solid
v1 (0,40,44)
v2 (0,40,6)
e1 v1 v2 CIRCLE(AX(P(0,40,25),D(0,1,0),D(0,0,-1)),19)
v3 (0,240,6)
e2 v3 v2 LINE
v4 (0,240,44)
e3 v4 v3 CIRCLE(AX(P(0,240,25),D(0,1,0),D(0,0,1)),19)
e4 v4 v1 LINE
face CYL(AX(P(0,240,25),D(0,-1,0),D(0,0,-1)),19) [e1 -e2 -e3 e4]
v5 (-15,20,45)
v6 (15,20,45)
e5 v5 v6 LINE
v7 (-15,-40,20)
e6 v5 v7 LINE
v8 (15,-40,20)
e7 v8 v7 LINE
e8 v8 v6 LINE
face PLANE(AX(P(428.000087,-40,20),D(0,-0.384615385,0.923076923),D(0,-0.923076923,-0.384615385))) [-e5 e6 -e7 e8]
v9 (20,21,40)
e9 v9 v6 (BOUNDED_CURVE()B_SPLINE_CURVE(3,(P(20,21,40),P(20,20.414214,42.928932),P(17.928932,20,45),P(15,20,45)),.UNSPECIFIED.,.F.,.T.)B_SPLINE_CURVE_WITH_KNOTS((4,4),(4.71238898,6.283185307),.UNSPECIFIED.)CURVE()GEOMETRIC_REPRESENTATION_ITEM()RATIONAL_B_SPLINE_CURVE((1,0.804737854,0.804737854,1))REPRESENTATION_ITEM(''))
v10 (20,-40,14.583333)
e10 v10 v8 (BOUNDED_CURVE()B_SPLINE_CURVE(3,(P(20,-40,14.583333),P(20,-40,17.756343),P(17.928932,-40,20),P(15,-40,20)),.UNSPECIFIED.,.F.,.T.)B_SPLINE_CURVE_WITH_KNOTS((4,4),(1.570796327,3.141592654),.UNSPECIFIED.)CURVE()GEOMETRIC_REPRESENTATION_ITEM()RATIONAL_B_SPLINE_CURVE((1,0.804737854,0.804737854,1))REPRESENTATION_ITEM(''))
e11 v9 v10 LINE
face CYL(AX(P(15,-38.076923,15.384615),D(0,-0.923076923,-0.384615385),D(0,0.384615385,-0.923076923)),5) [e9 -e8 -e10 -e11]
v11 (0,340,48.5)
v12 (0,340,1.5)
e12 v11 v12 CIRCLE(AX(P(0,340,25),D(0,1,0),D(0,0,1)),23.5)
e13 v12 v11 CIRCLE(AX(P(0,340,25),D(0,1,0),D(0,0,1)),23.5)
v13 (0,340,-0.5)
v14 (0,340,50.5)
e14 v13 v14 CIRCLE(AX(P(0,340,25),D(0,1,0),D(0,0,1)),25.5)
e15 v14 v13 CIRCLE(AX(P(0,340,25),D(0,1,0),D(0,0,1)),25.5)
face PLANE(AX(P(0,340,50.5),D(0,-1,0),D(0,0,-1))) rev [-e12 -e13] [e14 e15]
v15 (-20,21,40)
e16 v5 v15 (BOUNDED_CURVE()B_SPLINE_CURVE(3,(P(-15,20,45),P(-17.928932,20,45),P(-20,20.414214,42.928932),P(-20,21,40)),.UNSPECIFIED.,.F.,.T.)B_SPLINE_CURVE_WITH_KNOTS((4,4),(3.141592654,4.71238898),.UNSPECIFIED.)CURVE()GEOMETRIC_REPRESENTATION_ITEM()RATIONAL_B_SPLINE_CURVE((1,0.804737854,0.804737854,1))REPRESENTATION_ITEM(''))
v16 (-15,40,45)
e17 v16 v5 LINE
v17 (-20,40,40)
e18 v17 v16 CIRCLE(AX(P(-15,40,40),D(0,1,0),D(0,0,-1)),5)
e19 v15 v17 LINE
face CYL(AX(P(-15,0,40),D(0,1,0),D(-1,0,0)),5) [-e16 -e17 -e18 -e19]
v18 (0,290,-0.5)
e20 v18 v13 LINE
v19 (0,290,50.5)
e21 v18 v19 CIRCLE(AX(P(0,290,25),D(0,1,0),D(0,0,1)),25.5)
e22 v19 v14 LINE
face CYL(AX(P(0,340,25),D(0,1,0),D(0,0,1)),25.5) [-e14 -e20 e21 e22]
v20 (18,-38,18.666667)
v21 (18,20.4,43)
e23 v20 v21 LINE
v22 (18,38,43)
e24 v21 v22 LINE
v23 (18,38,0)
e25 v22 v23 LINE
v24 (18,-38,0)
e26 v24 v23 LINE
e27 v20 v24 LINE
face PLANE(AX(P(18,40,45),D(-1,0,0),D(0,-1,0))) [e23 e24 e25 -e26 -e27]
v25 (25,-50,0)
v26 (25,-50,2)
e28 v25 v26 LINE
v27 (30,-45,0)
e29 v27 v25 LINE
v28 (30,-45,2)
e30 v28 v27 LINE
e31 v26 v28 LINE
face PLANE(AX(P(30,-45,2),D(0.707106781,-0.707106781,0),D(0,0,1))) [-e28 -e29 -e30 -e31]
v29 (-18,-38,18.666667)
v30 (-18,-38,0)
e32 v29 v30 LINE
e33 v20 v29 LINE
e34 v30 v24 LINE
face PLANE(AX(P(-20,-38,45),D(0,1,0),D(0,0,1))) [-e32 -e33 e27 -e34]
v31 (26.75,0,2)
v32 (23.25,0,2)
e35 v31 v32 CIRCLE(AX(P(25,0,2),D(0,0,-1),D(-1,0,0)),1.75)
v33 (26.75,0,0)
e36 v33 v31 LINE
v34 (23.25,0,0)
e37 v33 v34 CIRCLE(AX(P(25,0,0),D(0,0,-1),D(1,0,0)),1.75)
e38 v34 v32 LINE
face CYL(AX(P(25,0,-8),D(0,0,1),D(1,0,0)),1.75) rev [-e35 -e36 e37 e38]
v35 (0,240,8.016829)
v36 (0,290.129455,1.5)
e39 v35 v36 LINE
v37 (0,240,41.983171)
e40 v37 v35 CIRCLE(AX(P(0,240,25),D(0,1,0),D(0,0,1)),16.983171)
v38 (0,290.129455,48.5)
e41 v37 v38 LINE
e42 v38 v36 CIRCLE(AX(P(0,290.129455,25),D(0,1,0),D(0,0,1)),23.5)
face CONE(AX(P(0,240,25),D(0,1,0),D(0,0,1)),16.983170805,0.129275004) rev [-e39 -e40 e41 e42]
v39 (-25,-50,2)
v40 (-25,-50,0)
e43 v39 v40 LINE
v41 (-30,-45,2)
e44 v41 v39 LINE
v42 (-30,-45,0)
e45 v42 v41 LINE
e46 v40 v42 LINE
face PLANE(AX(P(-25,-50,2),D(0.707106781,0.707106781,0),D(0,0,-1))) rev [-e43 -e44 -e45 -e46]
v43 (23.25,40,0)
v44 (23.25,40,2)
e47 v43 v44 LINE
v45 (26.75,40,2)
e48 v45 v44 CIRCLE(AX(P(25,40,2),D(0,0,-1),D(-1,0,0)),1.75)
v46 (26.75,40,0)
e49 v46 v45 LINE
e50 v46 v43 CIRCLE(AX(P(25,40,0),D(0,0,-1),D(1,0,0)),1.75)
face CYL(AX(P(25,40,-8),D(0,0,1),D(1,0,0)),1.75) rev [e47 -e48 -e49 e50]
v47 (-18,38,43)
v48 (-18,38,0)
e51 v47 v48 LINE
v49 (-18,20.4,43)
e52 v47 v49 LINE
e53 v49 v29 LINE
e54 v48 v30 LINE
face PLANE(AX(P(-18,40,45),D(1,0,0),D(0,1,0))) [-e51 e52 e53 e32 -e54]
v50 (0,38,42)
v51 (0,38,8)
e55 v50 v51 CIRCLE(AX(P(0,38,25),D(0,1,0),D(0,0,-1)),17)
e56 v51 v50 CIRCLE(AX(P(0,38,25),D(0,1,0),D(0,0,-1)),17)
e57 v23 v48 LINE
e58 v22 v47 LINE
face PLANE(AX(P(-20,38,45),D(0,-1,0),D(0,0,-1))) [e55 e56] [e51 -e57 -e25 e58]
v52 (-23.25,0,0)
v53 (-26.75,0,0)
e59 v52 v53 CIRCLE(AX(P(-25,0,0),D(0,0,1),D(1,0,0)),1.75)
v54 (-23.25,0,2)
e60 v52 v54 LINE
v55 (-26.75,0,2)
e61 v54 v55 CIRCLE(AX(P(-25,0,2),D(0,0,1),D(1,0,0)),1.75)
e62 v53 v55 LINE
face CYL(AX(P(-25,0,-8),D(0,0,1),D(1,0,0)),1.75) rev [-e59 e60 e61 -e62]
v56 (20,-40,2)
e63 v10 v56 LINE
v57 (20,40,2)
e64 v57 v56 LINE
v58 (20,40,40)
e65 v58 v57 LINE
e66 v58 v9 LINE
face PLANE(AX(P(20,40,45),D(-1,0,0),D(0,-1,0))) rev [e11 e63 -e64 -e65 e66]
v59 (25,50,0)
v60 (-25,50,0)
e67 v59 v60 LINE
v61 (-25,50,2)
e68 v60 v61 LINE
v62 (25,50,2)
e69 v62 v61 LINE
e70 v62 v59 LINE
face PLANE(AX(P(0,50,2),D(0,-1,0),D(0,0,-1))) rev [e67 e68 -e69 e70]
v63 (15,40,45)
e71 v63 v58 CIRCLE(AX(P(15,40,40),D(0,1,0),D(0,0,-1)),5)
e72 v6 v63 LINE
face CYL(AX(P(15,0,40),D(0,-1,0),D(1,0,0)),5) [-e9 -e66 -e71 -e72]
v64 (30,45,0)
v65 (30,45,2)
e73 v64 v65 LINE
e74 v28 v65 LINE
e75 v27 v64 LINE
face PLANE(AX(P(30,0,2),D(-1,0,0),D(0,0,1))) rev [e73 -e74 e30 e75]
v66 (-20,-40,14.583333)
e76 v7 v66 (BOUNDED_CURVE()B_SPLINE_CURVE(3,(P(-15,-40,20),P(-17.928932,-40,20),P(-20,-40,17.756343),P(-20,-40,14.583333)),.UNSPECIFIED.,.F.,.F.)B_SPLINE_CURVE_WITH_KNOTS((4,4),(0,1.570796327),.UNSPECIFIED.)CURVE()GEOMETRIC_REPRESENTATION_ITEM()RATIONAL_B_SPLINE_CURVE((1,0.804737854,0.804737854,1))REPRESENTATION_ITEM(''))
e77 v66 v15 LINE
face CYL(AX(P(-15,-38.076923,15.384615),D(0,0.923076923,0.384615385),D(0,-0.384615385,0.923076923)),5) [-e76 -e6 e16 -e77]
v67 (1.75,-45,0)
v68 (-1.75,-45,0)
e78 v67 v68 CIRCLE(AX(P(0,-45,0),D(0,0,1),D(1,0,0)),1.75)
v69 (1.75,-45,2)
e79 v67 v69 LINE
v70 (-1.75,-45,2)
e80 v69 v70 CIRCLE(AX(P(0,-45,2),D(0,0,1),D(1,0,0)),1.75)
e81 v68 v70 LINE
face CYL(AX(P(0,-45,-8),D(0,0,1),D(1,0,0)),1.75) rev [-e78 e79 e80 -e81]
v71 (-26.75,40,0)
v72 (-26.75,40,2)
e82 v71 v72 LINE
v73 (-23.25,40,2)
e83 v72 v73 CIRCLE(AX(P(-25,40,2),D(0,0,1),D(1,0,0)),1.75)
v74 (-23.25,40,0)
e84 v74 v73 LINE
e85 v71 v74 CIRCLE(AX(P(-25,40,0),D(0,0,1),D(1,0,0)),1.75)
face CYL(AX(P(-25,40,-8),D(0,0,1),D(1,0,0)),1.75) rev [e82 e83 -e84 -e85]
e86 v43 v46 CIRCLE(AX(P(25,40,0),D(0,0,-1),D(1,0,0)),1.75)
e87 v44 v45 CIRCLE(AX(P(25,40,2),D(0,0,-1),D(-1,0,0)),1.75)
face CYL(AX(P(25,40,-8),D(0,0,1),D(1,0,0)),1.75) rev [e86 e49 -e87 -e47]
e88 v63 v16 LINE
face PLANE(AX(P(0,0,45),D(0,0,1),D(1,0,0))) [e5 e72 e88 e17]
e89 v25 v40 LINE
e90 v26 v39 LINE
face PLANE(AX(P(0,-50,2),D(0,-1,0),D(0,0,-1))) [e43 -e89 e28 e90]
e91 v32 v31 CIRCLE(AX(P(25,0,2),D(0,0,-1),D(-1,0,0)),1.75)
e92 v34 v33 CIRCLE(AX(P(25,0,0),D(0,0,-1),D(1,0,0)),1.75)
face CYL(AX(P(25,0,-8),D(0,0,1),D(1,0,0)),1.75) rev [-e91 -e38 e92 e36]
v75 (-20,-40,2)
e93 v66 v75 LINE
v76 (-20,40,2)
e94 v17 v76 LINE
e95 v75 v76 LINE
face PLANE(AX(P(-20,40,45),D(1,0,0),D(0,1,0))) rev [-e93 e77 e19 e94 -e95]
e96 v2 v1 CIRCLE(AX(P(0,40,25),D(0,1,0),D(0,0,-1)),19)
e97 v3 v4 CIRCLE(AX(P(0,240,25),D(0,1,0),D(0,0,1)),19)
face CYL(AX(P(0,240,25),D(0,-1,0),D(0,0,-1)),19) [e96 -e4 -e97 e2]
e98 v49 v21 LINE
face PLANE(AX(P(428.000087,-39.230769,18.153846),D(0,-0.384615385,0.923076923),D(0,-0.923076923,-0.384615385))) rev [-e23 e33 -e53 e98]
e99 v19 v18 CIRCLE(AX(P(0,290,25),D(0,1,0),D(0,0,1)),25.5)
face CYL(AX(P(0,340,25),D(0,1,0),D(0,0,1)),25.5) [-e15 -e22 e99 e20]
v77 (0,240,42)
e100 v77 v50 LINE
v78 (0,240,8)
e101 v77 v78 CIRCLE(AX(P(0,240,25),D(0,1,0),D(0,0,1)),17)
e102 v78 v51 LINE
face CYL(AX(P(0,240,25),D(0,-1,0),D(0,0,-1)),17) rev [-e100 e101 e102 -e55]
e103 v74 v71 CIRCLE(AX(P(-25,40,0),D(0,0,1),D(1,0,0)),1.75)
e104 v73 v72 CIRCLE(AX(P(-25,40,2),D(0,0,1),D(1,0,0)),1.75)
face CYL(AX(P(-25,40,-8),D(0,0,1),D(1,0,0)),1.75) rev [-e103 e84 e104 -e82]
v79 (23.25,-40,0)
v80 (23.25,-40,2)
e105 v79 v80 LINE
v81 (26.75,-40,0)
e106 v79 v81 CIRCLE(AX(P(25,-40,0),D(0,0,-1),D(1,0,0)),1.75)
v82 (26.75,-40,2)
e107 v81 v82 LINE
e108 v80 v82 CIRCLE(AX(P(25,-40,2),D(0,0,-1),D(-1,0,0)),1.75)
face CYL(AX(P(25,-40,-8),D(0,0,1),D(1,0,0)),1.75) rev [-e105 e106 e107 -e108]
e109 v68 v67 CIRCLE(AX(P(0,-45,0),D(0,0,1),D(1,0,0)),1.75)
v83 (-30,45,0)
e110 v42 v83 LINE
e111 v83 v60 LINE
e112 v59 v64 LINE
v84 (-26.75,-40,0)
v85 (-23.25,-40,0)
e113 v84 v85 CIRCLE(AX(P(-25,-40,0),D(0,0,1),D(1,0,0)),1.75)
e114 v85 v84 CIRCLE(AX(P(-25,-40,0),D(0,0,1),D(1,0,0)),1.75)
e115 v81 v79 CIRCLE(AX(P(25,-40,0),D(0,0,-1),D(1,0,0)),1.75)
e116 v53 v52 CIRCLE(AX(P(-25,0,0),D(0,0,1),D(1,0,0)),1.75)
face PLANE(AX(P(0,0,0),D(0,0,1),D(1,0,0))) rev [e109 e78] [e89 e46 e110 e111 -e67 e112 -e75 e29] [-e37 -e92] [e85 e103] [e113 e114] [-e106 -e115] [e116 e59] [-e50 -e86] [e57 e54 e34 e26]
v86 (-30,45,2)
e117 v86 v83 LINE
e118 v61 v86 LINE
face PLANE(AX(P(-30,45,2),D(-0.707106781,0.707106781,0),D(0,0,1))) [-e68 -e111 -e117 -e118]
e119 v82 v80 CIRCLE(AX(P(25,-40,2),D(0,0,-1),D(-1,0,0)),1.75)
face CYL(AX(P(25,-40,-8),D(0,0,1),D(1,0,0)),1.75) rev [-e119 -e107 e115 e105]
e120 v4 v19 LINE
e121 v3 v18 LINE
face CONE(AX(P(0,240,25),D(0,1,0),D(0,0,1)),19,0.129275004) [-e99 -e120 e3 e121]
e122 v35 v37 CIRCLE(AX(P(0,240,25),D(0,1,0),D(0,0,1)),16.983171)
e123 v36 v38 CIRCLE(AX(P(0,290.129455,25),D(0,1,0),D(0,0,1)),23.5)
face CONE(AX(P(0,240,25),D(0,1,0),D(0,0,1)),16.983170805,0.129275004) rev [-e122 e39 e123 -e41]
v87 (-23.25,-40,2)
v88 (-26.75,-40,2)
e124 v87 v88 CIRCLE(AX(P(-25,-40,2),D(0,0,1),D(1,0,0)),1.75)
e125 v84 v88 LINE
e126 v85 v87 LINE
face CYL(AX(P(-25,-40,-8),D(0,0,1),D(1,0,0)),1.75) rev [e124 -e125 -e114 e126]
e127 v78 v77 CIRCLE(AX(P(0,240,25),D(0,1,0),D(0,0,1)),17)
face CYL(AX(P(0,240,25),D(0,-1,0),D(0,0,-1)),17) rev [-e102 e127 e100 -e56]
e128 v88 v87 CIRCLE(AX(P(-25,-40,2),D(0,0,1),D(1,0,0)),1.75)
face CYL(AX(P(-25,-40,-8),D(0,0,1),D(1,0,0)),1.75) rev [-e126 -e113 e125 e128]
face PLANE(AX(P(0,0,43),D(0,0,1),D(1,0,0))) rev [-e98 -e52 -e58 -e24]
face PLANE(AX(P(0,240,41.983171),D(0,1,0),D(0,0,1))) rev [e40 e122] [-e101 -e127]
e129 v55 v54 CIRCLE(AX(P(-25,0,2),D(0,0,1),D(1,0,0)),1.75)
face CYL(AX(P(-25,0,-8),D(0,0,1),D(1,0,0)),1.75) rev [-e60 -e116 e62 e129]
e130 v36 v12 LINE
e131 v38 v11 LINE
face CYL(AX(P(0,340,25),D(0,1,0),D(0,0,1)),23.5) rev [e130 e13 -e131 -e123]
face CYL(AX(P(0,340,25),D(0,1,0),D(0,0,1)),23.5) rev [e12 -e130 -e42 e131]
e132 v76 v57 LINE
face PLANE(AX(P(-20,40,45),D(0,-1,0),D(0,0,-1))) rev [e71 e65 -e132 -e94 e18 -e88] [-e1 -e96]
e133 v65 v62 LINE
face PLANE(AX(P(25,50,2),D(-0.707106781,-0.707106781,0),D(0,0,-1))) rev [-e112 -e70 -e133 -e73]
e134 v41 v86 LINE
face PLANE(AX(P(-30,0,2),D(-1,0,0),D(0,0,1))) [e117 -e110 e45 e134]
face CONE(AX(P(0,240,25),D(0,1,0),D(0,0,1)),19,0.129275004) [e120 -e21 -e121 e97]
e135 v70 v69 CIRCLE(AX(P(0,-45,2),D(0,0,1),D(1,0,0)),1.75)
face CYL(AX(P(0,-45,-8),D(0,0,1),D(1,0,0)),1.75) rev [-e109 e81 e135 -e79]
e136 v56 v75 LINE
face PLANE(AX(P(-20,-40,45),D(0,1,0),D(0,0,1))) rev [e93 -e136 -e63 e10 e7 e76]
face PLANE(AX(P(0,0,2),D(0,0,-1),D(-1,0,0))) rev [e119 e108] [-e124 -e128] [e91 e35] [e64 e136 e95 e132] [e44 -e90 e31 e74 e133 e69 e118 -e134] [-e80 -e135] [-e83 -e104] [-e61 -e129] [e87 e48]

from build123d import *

# Parameters (mm, degrees)
SKETCH1_W               = 40
SKETCH1_H               = 80
BOSS_EXTRUDE1_DEPTH     = 45
SKETCH2_R               = 19
BOSS_EXTRUDE2_DEPTH     = 200
CUT_EXTRUDE1_DEPTH      = 248.436860633
CUT_EXTRUDE1_DEPTH_BACK = 248.436860633
SHELL1_T                = -2
SKETCH4_W               = 60
SKETCH4_H               = 100
SKETCH4_W_2             = 40
SKETCH4_H_2             = 80
BOSS_EXTRUDE3_DEPTH     = 2
CHAMFER1_SIZE           = 5
SKETCH5_R               = 1.75
CUT_EXTRUDE2_DEPTH      = 10
SKETCH6_R               = 1.75
CUT_EXTRUDE3_DEPTH      = 10
FILLET1_R               = 5


with BuildPart() as part:
    # Sketch1 → Boss-Extrude1 (new body)
    with BuildSketch(Plane.XY):
        Rectangle(SKETCH1_W, SKETCH1_H)
    extrude(amount=BOSS_EXTRUDE1_DEPTH)

    # Sketch2 → Boss-Extrude2 (add)
    with BuildSketch(Plane(origin=(0, 40, 0), x_dir=(1, 0, 0), z_dir=(0, 1, 0))):
        with Locations(Location((0, -25, 0), (0, 0, 90))):
            Circle(SKETCH2_R)
    extrude(amount=BOSS_EXTRUDE2_DEPTH)

    # Sketch3 → Cut-Extrude1 (cut, two sides: drawn at the far end of the back side and taken through both)
    with BuildSketch(Plane(origin=(20, 0, 0), x_dir=(0, 0, -1), z_dir=(1, 0, 0)).offset(-CUT_EXTRUDE1_DEPTH_BACK)):
        Polygon((200.08758149, -568.210195577), (-20, -40), (-45, 20), (-265.08758149, 548.210195577), (-1321.507972644, 108.035032596), (-856.332809663, -1008.385358557), align=None)
    extrude(amount=CUT_EXTRUDE1_DEPTH + CUT_EXTRUDE1_DEPTH_BACK, mode=Mode.SUBTRACT)

    # Shell1
    shell1_openings = [part.faces().sort_by_distance(p)[0] for p in [
        (0, 240, 25),
        (0, 0, 0),
    ]]
    offset(amount=SHELL1_T, openings=shell1_openings, kind=Kind.INTERSECTION)

    # Sketch4 → Boss-Extrude3 (add)
    with BuildSketch(Plane(origin=(0, 0, 0), x_dir=(-1, 0, 0), z_dir=(0, 0, -1))):
        Rectangle(SKETCH4_W, SKETCH4_H)
        Rectangle(SKETCH4_W_2, SKETCH4_H_2, mode=Mode.SUBTRACT)
    extrude(amount=-BOSS_EXTRUDE3_DEPTH)

    # Chamfer1
    chamfer1_edges = [part.edges().sort_by_distance(p)[0] for p in [
        (-30, -50, 1),
        (30, -50, 1),
        (30, 50, 1),
        (-30, 50, 1),
    ]]
    chamfer(chamfer1_edges, length=CHAMFER1_SIZE)

    # Sketch5 → Cut-Extrude2 (cut)
    with BuildSketch(Plane.XY.offset(2)):
        with Locations((-25, 0)):
            Circle(SKETCH5_R)
        with Locations((-25, 40)):
            Circle(SKETCH5_R)
        with Locations((-25, -40)):
            Circle(SKETCH5_R)
    cut_extrude2 = extrude(amount=-CUT_EXTRUDE2_DEPTH, mode=Mode.SUBTRACT)

    # Mirror1: Cut-Extrude2 across plane
    add(cut_extrude2.mirror(Plane(origin=(0, 0, 0), x_dir=(0, 0, 1), z_dir=(1, 0, 0))), mode=Mode.SUBTRACT)

    # Sketch6 → Cut-Extrude3 (cut)
    with BuildSketch(Plane.XY.offset(2)):
        with Locations((0, -45)):
            Circle(SKETCH6_R)
    extrude(amount=-CUT_EXTRUDE3_DEPTH, mode=Mode.SUBTRACT)

    # Sketch7 → Revolve1 (revolve)
    with BuildSketch(Plane(origin=(0, 0, 0), x_dir=(0, 0, -1), z_dir=(1, 0, 0))):
        Polygon((-44, 240), (-50.5, 290), (-50.5, 340), (-48.5, 340), (-48.5, 290.129455343), (-41.983170805, 240), align=None)
    revolve(axis=Axis((0, 340, 25), (0, -1, 0)))

    # Fillet1
    fillet1_edges = [part.edges().sort_by_distance(p)[0] for p in [
        (-20, 30, 45),
        (20, 30, 45),
        (20, -10, 32.5),
        (-20, -10, 32.5),
    ]]
    fillet(fillet1_edges, radius=FILLET1_R)


solid = part.part
